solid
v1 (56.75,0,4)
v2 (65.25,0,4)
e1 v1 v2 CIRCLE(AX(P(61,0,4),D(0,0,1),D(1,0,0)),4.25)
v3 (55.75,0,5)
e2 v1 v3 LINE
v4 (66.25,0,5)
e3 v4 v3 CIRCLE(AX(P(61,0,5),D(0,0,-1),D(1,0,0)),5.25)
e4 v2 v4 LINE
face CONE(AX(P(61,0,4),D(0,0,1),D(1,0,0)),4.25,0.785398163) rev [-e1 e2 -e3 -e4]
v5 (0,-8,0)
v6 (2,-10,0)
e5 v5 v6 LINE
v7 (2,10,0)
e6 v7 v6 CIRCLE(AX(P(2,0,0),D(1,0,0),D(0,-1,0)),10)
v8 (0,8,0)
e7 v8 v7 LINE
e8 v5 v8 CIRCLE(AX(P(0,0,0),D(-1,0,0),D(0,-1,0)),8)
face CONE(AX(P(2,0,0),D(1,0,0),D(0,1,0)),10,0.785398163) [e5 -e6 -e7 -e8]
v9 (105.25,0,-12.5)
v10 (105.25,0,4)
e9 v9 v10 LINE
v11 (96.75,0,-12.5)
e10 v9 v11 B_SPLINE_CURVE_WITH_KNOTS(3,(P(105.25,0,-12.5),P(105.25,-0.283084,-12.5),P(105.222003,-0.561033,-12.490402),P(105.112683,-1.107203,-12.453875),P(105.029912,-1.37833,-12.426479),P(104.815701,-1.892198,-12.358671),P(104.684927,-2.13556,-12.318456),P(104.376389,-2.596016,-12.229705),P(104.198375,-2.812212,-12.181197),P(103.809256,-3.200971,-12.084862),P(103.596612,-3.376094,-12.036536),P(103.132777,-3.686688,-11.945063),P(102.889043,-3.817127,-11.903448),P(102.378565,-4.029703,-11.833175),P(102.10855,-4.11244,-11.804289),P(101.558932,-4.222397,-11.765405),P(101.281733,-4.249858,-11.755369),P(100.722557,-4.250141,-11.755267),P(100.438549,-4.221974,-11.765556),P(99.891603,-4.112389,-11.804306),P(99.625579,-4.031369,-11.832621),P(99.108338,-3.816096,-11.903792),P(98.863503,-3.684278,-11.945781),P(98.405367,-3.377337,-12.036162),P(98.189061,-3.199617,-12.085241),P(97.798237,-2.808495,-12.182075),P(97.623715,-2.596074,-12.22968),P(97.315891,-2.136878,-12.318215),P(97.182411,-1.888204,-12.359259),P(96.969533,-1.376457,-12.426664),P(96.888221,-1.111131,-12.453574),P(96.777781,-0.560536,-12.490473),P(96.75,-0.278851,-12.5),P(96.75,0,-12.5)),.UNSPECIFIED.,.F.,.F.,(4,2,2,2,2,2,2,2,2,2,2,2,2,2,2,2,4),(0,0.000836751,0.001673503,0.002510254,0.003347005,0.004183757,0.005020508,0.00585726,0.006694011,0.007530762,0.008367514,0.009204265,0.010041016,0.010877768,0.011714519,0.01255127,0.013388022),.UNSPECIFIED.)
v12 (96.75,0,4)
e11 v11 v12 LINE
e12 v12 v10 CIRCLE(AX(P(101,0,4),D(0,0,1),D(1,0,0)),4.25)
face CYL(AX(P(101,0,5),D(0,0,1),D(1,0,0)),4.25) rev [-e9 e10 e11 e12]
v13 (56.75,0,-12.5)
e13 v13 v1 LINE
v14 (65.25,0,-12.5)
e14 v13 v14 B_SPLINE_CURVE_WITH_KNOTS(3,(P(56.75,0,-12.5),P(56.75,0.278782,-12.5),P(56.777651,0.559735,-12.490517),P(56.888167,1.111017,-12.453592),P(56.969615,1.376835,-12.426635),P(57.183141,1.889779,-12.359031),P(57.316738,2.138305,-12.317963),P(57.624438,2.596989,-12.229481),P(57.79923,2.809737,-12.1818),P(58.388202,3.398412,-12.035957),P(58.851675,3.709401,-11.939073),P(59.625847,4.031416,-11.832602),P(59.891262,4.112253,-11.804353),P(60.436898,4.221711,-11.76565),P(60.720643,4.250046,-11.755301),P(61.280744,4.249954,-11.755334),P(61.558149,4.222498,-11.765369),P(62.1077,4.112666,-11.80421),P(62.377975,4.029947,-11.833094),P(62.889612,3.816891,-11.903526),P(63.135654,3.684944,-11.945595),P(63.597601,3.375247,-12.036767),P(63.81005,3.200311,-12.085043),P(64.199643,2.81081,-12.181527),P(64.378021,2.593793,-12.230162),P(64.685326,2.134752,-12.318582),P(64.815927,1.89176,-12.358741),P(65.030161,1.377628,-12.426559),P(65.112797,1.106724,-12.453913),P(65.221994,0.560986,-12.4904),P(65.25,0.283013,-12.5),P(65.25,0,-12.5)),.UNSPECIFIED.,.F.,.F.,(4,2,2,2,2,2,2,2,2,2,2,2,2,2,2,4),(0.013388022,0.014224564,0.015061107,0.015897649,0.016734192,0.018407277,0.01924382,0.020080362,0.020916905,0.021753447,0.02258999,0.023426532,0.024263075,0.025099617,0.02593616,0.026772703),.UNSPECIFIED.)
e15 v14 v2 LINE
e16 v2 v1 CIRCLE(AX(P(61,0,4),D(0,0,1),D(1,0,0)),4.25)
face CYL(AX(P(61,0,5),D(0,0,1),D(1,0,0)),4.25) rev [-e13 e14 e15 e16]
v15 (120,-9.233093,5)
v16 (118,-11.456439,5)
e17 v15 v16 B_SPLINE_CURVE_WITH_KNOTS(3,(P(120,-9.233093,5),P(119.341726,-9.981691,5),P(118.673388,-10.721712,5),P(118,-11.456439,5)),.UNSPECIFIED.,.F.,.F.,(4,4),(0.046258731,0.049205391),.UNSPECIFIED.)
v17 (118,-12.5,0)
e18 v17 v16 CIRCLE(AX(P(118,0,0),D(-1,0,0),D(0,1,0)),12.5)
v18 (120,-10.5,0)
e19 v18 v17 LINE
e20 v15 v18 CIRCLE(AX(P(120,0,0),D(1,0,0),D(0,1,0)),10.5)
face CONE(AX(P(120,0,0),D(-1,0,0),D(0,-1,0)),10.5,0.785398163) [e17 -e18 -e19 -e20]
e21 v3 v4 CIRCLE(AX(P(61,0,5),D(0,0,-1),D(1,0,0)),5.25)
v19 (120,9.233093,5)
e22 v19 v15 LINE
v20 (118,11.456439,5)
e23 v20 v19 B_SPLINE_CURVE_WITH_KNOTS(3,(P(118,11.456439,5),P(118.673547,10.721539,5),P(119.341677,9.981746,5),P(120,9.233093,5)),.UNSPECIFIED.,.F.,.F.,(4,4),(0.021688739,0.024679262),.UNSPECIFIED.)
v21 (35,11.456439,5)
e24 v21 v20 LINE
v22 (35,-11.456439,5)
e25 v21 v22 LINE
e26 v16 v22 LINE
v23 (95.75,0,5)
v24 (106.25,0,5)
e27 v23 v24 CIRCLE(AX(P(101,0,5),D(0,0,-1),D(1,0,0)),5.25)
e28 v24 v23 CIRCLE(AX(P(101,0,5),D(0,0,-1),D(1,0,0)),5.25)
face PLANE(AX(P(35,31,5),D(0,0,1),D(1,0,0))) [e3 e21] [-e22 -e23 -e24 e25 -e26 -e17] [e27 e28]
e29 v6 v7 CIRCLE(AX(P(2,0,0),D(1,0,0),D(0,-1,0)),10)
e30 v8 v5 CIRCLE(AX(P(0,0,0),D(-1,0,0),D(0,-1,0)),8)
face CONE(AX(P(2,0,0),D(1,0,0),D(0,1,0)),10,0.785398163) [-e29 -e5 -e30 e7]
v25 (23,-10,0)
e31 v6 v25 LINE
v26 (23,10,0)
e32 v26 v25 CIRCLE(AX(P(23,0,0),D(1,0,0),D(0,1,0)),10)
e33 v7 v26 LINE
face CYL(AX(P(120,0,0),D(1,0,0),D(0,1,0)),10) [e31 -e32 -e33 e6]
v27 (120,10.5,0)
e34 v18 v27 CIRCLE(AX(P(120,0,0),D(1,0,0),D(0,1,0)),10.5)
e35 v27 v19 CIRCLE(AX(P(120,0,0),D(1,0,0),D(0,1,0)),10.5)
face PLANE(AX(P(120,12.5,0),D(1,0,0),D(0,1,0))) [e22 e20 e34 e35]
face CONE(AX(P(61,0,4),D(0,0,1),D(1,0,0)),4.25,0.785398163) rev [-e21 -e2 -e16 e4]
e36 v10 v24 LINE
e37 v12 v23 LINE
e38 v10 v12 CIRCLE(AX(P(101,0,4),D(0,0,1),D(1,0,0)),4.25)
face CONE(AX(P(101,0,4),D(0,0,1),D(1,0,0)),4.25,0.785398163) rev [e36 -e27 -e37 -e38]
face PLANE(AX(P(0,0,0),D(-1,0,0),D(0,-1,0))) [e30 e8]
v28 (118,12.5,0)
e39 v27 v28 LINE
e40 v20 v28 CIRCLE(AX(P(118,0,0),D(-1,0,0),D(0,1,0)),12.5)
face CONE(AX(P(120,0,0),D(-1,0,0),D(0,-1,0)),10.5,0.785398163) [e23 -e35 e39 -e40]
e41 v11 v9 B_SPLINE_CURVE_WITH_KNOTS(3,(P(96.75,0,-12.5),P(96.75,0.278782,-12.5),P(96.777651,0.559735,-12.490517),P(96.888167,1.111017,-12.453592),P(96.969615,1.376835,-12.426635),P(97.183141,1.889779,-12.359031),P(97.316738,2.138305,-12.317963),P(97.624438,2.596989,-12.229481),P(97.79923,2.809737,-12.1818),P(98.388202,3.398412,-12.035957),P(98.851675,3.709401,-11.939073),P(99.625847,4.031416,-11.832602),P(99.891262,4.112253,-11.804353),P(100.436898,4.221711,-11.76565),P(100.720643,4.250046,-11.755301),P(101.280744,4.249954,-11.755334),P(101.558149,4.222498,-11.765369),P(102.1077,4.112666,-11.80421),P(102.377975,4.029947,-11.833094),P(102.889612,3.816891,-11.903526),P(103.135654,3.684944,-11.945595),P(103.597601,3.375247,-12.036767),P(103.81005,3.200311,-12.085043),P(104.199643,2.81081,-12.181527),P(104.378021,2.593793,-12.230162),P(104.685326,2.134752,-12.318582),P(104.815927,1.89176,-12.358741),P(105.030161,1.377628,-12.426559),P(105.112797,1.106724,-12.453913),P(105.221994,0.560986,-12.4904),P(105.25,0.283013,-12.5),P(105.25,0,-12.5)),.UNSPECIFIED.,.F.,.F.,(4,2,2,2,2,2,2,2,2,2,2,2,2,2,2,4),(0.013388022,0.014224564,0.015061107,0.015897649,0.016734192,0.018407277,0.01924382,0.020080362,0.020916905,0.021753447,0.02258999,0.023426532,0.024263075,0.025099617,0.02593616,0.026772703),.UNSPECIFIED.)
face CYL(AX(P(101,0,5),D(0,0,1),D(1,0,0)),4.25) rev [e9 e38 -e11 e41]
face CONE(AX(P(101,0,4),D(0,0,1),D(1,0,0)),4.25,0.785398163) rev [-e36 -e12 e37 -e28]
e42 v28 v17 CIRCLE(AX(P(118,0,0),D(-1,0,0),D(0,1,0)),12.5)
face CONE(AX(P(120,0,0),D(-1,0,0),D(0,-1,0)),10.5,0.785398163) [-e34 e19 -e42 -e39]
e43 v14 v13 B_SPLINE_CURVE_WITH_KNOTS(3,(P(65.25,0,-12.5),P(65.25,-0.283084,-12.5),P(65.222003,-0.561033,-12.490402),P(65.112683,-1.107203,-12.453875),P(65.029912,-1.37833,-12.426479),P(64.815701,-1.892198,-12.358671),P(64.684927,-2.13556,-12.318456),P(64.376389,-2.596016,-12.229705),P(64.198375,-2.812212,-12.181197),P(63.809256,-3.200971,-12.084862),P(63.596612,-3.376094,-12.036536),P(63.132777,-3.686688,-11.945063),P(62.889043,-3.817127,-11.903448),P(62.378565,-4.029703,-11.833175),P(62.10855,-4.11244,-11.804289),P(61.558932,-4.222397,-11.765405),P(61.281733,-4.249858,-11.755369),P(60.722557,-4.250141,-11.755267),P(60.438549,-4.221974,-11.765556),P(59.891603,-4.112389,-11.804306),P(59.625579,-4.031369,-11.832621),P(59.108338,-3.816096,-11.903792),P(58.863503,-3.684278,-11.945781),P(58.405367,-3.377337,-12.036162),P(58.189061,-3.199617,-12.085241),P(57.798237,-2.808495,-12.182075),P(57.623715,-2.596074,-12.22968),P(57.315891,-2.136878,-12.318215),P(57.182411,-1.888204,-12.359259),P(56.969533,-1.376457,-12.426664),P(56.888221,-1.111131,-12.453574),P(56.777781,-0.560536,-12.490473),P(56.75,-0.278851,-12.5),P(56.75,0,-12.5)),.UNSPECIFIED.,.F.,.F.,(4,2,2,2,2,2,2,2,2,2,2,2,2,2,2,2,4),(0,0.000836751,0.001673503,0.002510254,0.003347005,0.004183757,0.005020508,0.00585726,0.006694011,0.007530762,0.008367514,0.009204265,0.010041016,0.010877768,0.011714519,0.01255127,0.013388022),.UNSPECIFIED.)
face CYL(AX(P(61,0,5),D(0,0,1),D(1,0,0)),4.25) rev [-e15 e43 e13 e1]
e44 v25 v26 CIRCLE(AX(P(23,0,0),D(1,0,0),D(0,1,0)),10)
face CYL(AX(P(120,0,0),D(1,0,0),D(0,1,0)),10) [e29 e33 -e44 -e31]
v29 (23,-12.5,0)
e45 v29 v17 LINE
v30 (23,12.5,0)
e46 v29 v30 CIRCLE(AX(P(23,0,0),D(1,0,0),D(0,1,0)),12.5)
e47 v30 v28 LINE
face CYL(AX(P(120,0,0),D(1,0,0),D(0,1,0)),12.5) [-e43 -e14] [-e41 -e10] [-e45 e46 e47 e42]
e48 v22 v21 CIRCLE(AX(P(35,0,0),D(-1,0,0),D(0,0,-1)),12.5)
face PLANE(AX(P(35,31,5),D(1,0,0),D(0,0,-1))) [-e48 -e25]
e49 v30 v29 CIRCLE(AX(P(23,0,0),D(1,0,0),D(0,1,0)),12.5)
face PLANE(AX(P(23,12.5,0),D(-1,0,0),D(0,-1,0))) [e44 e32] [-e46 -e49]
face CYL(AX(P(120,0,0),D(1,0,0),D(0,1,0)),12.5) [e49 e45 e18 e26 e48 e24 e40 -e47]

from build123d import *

# Parameters (mm, degrees)
CHAMFER_1_SIZE           = 2
CUT_EXTRUDE_1_DEPTH      = 31
CUT_EXTRUDE_1_DEPTH_BACK = 20
SKETCH_2_W               = 91.624519514
SKETCH_2_H               = 25.767863676
HOLE_WIZARD_M10_1_D      = 8.5
HOLE_WIZARD_M10_1_DEPTH  = 27.5
HOLE_WIZARD_M10_1_TIP    = 2.553657631
CHAMFER_3_SIZE           = 1


with BuildPart() as part:
    # 草图1 → 旋转2 (revolve)
    with BuildSketch(Plane.XY):
        Polygon((0, 0), (0, 10), (23, 10), (23, 12.5), (120, 12.5), (120, 0), align=None)
    revolve(axis=Axis((120, 0, 0), (-1, 0, 0)))

    # 倒角1
    chamfer_1_edges = [part.edges().sort_by_distance(p)[0] for p in [
        (120, -12.5, 0),
        (0, -10, 0),
    ]]
    chamfer(chamfer_1_edges, length=CHAMFER_1_SIZE)

    # 草图2 → 切除-拉伸1 (cut, two sides: drawn at the far end of the back side and taken through both)
    with BuildSketch(Plane(origin=(0, 0, 0), x_dir=(1, 0, 0), z_dir=(0, 1, 0)).offset(-CUT_EXTRUDE_1_DEPTH_BACK)):
        with Locations((80.812259757, -17.883931838)):
            Rectangle(SKETCH_2_W, SKETCH_2_H)
    extrude(amount=CUT_EXTRUDE_1_DEPTH + CUT_EXTRUDE_1_DEPTH_BACK, mode=Mode.SUBTRACT)

    # M10 螺纹孔1
    with Locations(Plane.XY.offset(5)):
        with Locations((61, 0), (101, 0)):
            Hole(HOLE_WIZARD_M10_1_D / 2, depth=HOLE_WIZARD_M10_1_DEPTH)
            with Locations((0, 0, -(HOLE_WIZARD_M10_1_DEPTH + HOLE_WIZARD_M10_1_TIP / 2))):  # 118° drill point
                Cone(0, HOLE_WIZARD_M10_1_D / 2, HOLE_WIZARD_M10_1_TIP, mode=Mode.SUBTRACT)

    # 倒角3
    chamfer_3_edges = [part.edges().sort_by_distance(p)[0] for p in [
        (105.25, 0, 5),
        (65.25, 0, 5),
    ]]
    chamfer(chamfer_3_edges, length=CHAMFER_3_SIZE)


solid = part.part
